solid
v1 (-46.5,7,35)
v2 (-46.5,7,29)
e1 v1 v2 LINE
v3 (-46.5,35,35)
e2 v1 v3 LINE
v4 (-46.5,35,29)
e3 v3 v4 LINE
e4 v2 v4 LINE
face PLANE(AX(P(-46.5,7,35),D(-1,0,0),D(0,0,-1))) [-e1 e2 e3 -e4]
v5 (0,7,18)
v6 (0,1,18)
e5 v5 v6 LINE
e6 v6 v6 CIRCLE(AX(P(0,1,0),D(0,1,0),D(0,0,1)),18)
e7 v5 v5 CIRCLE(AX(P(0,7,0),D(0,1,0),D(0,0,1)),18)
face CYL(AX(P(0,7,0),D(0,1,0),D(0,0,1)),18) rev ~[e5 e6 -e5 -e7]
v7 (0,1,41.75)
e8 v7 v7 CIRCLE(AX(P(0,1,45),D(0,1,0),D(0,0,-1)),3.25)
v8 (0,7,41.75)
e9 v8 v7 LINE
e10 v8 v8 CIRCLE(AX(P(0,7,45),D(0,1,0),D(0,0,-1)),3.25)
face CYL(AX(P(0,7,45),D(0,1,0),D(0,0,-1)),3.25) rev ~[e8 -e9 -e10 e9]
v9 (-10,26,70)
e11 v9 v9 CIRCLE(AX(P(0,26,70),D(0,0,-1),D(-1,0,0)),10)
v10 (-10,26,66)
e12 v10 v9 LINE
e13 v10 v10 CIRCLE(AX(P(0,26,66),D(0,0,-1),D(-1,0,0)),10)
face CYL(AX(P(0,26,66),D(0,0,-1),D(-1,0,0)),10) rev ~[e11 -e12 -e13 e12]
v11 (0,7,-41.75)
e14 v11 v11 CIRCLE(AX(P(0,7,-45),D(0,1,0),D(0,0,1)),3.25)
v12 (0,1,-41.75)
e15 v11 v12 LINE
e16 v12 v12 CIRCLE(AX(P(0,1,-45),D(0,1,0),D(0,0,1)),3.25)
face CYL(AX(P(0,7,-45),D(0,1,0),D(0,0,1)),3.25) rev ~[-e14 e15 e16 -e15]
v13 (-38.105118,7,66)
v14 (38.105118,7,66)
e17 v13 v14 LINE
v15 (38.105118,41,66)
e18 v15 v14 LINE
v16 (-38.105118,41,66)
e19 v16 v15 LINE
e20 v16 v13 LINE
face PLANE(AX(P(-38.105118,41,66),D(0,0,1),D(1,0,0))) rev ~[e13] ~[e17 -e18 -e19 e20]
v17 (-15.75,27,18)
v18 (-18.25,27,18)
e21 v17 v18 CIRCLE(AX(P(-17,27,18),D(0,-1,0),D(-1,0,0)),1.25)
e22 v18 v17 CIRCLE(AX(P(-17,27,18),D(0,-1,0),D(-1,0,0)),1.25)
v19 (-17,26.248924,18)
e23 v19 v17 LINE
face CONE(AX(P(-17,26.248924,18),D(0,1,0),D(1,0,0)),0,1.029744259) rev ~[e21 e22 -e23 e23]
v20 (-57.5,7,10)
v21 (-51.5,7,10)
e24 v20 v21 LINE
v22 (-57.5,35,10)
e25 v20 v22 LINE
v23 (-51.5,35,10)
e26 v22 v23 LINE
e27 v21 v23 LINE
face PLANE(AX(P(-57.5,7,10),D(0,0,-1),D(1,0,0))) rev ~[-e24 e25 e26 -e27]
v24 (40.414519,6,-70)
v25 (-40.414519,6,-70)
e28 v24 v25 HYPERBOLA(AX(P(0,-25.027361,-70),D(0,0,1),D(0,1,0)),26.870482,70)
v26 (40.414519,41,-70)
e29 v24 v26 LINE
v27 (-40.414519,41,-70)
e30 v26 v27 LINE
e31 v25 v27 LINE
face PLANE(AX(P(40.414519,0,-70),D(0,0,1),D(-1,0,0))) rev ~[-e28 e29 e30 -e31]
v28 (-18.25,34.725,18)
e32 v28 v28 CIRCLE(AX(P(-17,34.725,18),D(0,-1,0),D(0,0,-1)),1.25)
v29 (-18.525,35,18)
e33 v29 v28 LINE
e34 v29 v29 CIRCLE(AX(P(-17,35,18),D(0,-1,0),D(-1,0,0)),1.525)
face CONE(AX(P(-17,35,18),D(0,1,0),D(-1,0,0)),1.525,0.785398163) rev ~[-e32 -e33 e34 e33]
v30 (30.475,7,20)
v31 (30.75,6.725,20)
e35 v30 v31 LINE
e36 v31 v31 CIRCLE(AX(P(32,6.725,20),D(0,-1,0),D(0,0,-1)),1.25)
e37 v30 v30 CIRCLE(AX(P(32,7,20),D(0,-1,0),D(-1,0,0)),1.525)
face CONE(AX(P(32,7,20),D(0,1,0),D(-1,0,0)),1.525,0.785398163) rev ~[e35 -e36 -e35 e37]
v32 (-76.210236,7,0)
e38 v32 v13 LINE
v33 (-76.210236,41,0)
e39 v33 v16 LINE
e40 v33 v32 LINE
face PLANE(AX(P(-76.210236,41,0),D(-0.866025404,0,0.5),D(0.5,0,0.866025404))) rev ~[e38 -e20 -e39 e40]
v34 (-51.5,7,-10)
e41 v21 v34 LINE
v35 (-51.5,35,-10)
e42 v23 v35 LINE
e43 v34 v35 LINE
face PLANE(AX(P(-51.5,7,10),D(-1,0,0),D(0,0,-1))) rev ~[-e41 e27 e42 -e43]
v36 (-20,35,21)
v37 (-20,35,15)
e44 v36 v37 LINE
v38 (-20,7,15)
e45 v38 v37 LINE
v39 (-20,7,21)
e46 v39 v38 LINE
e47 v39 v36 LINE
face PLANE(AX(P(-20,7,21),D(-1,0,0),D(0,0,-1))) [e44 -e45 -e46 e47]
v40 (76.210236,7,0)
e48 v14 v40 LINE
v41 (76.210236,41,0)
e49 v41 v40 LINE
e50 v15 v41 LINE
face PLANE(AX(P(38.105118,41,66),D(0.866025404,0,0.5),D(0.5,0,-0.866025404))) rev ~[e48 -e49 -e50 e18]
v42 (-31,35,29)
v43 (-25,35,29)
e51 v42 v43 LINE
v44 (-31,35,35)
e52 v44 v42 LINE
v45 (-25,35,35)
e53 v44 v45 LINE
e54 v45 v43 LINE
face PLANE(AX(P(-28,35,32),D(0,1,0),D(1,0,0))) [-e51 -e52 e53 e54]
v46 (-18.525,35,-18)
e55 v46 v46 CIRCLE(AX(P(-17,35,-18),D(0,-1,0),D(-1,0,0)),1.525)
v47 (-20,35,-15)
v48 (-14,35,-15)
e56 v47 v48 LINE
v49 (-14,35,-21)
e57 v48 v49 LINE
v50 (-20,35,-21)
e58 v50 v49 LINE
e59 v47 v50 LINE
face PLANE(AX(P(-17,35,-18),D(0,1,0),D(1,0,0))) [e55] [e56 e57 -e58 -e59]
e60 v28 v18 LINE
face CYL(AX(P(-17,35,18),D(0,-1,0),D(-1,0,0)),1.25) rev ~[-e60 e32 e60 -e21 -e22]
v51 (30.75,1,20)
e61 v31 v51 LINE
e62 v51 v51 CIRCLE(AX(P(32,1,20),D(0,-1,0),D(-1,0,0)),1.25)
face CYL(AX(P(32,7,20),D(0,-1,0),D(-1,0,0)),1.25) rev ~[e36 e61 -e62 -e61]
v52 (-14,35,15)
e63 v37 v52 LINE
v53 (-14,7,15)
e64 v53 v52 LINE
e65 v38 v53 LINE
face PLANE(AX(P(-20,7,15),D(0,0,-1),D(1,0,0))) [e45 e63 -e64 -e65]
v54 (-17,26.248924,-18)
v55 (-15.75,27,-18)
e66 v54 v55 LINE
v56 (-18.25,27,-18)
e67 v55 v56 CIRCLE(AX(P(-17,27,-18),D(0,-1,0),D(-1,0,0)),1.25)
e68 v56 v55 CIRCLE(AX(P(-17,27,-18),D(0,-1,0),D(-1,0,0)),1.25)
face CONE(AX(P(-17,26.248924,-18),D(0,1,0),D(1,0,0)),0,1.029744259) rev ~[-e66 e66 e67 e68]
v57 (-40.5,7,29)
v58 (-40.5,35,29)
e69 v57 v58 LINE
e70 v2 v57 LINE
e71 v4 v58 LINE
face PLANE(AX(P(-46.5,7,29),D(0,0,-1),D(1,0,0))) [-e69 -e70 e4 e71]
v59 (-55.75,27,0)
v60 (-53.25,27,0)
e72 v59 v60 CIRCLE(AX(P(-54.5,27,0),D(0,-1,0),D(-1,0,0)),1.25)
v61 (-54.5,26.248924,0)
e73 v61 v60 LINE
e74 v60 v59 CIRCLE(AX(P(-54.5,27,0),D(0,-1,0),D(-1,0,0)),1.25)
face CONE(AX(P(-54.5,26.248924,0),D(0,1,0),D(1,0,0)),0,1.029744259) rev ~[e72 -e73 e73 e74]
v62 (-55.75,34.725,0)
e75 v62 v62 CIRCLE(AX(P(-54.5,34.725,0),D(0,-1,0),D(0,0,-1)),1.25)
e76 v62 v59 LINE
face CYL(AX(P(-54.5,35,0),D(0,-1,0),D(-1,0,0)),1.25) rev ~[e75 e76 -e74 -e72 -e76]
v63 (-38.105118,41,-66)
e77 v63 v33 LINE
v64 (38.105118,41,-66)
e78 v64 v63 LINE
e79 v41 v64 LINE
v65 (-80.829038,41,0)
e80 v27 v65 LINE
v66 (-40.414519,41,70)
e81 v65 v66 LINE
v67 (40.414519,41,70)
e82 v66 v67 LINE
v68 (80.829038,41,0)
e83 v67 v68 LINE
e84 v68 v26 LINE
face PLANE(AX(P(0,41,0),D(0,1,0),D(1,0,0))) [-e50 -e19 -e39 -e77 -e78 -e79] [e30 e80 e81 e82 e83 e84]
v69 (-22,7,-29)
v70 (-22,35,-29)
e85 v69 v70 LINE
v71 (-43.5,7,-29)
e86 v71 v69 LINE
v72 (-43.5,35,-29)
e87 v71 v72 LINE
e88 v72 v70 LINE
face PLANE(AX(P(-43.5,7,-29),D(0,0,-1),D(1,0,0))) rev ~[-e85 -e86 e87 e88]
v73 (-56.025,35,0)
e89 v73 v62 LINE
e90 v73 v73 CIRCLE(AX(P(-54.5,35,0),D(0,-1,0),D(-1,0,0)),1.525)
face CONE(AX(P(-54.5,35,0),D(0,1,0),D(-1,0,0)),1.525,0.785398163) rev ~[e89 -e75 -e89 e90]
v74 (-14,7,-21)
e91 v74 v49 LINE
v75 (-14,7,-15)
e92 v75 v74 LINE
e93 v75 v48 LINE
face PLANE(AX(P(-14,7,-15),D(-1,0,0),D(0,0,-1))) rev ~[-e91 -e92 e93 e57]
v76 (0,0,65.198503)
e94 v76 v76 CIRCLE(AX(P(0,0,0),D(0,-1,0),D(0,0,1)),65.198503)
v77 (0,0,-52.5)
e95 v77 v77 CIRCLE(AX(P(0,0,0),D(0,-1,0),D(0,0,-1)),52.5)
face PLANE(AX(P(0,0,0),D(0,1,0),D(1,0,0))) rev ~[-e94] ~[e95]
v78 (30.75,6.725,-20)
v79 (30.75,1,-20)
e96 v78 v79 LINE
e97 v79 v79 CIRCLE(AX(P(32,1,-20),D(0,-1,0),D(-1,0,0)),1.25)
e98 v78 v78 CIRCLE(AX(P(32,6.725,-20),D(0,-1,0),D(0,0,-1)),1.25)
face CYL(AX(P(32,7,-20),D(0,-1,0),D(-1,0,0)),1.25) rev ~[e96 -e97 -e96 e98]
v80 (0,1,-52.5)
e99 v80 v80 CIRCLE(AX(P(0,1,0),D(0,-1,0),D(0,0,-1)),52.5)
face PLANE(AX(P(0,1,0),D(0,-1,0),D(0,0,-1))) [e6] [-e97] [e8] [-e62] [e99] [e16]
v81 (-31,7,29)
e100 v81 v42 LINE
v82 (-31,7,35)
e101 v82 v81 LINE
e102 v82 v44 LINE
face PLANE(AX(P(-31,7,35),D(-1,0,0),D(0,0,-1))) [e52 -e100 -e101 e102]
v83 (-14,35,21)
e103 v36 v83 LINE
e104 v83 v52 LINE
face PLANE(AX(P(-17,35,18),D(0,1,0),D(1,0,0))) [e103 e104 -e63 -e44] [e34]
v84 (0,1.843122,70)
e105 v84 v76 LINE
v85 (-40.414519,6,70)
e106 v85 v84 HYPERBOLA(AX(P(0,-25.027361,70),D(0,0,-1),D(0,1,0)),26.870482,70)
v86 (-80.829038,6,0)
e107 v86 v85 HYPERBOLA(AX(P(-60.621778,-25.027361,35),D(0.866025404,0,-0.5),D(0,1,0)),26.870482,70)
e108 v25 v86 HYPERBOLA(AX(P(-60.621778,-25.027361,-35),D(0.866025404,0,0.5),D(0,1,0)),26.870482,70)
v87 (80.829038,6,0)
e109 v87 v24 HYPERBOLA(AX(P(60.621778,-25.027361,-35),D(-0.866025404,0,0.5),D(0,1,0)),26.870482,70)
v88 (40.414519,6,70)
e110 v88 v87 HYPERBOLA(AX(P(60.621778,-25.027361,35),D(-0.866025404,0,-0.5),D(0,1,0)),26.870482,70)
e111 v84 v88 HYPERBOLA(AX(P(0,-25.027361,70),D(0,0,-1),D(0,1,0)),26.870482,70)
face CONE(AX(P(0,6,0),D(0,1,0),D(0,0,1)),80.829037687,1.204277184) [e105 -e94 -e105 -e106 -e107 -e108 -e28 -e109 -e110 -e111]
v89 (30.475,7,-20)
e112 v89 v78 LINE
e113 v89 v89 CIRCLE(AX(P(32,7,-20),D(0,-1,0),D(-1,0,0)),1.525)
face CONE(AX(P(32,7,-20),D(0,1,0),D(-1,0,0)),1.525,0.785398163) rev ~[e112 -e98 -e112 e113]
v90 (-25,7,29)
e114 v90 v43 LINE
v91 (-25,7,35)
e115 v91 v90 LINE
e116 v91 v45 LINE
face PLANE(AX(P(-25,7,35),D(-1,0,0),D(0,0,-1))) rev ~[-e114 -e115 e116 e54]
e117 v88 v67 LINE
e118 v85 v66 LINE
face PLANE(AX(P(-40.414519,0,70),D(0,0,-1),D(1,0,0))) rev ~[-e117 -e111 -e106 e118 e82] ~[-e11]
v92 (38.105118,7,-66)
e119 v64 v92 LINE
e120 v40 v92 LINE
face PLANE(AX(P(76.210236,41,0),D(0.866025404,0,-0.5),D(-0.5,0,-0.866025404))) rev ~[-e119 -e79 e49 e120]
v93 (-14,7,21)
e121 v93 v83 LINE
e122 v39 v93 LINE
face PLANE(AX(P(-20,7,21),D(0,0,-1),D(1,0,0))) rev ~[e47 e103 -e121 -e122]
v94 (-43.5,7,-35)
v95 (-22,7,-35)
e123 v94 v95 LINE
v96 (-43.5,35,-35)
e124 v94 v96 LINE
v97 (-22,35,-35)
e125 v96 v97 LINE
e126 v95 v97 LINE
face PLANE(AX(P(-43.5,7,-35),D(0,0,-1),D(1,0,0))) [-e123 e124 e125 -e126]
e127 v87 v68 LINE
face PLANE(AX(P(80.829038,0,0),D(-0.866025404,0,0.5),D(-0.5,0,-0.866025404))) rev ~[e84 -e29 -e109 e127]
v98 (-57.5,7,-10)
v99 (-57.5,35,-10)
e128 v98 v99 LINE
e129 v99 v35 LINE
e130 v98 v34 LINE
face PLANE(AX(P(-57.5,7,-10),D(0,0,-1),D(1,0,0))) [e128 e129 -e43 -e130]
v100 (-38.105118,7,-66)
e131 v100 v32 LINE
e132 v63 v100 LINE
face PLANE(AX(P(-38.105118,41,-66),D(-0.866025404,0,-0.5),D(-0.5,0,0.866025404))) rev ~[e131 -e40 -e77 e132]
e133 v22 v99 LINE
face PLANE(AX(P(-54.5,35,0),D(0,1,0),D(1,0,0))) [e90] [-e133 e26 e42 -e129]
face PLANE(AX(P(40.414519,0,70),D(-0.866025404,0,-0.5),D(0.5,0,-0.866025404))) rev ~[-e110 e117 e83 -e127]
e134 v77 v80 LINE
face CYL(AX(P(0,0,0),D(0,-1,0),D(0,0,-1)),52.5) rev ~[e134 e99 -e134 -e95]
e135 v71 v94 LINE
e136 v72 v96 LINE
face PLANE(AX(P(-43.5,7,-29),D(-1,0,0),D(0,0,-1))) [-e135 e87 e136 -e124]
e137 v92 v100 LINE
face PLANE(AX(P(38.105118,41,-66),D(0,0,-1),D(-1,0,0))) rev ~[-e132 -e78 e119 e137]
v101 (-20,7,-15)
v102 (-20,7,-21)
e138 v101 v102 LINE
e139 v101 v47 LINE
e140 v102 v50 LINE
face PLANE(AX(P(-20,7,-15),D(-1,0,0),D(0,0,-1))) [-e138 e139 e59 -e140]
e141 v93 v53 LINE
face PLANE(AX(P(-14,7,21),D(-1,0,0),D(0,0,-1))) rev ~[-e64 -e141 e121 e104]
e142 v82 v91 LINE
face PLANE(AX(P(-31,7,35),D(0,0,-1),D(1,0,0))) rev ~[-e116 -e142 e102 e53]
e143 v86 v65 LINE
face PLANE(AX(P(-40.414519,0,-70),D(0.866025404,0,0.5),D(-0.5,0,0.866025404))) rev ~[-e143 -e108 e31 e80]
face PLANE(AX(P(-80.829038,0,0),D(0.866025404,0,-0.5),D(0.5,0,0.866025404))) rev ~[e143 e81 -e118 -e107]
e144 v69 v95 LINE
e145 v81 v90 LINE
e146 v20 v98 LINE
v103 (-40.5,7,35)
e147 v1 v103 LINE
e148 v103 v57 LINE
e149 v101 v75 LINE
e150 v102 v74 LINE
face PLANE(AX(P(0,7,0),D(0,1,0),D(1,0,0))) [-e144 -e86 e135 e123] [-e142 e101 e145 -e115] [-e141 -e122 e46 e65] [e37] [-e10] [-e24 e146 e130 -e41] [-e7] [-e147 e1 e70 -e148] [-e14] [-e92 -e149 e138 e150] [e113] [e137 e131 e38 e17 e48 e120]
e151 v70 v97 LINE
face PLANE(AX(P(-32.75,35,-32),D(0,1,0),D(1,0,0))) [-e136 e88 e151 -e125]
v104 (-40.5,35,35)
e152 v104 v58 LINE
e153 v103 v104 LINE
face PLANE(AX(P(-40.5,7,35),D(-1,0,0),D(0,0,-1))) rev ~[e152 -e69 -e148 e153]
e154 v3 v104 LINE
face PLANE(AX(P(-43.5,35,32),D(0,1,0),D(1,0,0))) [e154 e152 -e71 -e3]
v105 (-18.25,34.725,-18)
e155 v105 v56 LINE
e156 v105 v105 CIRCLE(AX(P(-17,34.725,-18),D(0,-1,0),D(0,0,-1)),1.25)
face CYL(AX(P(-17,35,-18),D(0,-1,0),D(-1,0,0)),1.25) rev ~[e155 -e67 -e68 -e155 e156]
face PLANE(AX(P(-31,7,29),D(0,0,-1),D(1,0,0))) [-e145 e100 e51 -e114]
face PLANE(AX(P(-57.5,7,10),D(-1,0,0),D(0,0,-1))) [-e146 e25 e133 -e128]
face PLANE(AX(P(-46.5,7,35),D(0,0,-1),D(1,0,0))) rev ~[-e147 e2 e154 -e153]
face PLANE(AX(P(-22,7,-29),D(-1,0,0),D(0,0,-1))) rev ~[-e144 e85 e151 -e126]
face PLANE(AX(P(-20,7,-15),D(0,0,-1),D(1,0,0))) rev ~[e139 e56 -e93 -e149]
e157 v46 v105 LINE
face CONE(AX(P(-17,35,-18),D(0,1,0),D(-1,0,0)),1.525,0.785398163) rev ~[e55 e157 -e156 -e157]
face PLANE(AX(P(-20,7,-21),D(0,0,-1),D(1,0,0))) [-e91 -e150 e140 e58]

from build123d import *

# Parameters (mm, degrees)
BOSS_EXTRUDE1_DEPTH         = 41
CUT_EXTRUDE1_DEPTH          = 34
SKETCH4_R                   = 52.5
CUT_EXTRUDE2_DEPTH          = 1
SKETCH5_W                   = 21.5
SKETCH5_H                   = 6
SKETCH5_W_2                 = 6
SKETCH5_H_2                 = 20
BOSS_EXTRUDE2_DEPTH         = 28
SKETCH6_R                   = 18
CUT_EXTRUDE3_DEPTH          = 28
SKETCH7_R                   = 3.25
CUT_EXTRUDE4_DEPTH          = 28
M3_TAPPED_HOLE1_D           = 2.5
M3_TAPPED_HOLE1_CSINK_D     = 3.05
M3_TAPPED_HOLE1_CSINK_ANGLE = 90
M3_TAPPED_HOLE2_D           = 2.5
M3_TAPPED_HOLE2_DEPTH       = 8
M3_TAPPED_HOLE2_CSINK_D     = 3.05
M3_TAPPED_HOLE2_CSINK_ANGLE = 90
M3_TAPPED_HOLE2_TIP         = 0.751075774
SKETCH8_R                   = 10
CUT_EXTRUDE5_DEPTH          = 28


with BuildPart() as part:
    # Sketch1 → Boss-Extrude1 (new body)
    with BuildSketch(Plane(origin=(0, 0, 0), x_dir=(1, 0, 0), z_dir=(0, 1, 0))):
        Polygon((-40.414518843, 70), (-80.829037687, 0), (-40.414518843, -70), (40.414518843, -70), (80.829037687, 0), (40.414518843, 70), align=None)
    extrude(amount=BOSS_EXTRUDE1_DEPTH)

    # Sketch2 → Cut-Extrude1 (cut)
    with BuildSketch(Plane(origin=(0, 41, 0), x_dir=(1, 0, 0), z_dir=(0, 1, 0))):
        Polygon((38.105117767, -66), (76.210235533, 0), (38.105117767, 66), (-38.105117767, 66), (-76.210235533, 0), (-38.105117767, -66), align=None)
    extrude(amount=-CUT_EXTRUDE1_DEPTH, mode=Mode.SUBTRACT)

    # Sketch3 → Cut-Revolve1 (revolve, cut)
    with BuildSketch(Plane.XY, mode=Mode.PRIVATE) as cut_revolve1_sk:
        Polygon((-80.829037687, 6), (-65.198503298, 0), (-80.829037687, 0), align=None)
    revolve(cut_revolve1_sk.sketch.rotate(Axis((0, 62.900603769, 0), (0, -1, 0)), 270), axis=Axis((0, 62.900603769, 0), (0, -1, 0)), mode=Mode.SUBTRACT)

    # Sketch4 → Cut-Extrude2 (cut)
    with BuildSketch(Plane.XZ):
        with Locations(Location((0, 0, 0), (0, 0, 270))):
            Circle(SKETCH4_R)
    extrude(amount=-CUT_EXTRUDE2_DEPTH, mode=Mode.SUBTRACT)

    # Sketch5 → Boss-Extrude2 (add)
    with BuildSketch(Plane(origin=(0, 7, 0), x_dir=(1, 0, 0), z_dir=(0, 1, 0))):
        with Locations((-32.75, 32)):
            Rectangle(SKETCH5_W, SKETCH5_H)
        with Locations((-54.5, 0)):
            Rectangle(SKETCH5_W_2, SKETCH5_H_2)
        with Locations((-43.5, -32)):
            Rectangle(SKETCH5_W_2, SKETCH5_H)
        with Locations((-28, -32)):
            Rectangle(SKETCH5_W_2, SKETCH5_H)
        with Locations((-17, 18)):
            Rectangle(SKETCH5_W_2, SKETCH5_H)
        with Locations((-17, -18)):
            Rectangle(SKETCH5_W_2, SKETCH5_H)
    extrude(amount=BOSS_EXTRUDE2_DEPTH)

    # Sketch6 → Cut-Extrude3 (cut)
    with BuildSketch(Plane(origin=(0, 7, 0), x_dir=(1, 0, 0), z_dir=(0, 1, 0))):
        with Locations(Location((0, 0, 0), (0, 0, 270))):
            Circle(SKETCH6_R)
    extrude(amount=-CUT_EXTRUDE3_DEPTH, mode=Mode.SUBTRACT)

    # Sketch7 → Cut-Extrude4 (cut)
    with BuildSketch(Plane(origin=(0, 7, 0), x_dir=(1, 0, 0), z_dir=(0, 1, 0))):
        with Locations(Location((0, 45, 0), (0, 0, 270))):
            Circle(SKETCH7_R)
        with Locations(Location((0, -45, 0), (0, 0, 90))):
            Circle(SKETCH7_R)
    extrude(amount=-CUT_EXTRUDE4_DEPTH, mode=Mode.SUBTRACT)

    # M3 Tapped Hole1 (through all)
    with Locations(Plane(origin=(0, 7, 0), x_dir=(1, 0, 0), z_dir=(0, 1, 0))):
        with Locations((32, 20), (32, -20)):
            CounterSinkHole(M3_TAPPED_HOLE1_D / 2, M3_TAPPED_HOLE1_CSINK_D / 2, counter_sink_angle=M3_TAPPED_HOLE1_CSINK_ANGLE)

    # M3 Tapped Hole2
    with Locations(Plane(origin=(0, 35, 0), x_dir=(1, 0, 0), z_dir=(0, 1, 0))):
        with Locations((-54.5, 0), (-17, 18), (-17, -18)):
            CounterSinkHole(M3_TAPPED_HOLE2_D / 2, M3_TAPPED_HOLE2_CSINK_D / 2, depth=M3_TAPPED_HOLE2_DEPTH, counter_sink_angle=M3_TAPPED_HOLE2_CSINK_ANGLE)
            with Locations((0, 0, -(M3_TAPPED_HOLE2_DEPTH + M3_TAPPED_HOLE2_TIP / 2))):  # 118° drill point
                Cone(0, M3_TAPPED_HOLE2_D / 2, M3_TAPPED_HOLE2_TIP, mode=Mode.SUBTRACT)

    # Sketch8 → Cut-Extrude5 (cut)
    with BuildSketch(Plane(origin=(0, 0, 66), x_dir=(-1, 0, 0), z_dir=(0, 0, -1))):
        with Locations((0, 26)):
            Circle(SKETCH8_R)
    extrude(amount=-CUT_EXTRUDE5_DEPTH, mode=Mode.SUBTRACT)


solid = part.part
